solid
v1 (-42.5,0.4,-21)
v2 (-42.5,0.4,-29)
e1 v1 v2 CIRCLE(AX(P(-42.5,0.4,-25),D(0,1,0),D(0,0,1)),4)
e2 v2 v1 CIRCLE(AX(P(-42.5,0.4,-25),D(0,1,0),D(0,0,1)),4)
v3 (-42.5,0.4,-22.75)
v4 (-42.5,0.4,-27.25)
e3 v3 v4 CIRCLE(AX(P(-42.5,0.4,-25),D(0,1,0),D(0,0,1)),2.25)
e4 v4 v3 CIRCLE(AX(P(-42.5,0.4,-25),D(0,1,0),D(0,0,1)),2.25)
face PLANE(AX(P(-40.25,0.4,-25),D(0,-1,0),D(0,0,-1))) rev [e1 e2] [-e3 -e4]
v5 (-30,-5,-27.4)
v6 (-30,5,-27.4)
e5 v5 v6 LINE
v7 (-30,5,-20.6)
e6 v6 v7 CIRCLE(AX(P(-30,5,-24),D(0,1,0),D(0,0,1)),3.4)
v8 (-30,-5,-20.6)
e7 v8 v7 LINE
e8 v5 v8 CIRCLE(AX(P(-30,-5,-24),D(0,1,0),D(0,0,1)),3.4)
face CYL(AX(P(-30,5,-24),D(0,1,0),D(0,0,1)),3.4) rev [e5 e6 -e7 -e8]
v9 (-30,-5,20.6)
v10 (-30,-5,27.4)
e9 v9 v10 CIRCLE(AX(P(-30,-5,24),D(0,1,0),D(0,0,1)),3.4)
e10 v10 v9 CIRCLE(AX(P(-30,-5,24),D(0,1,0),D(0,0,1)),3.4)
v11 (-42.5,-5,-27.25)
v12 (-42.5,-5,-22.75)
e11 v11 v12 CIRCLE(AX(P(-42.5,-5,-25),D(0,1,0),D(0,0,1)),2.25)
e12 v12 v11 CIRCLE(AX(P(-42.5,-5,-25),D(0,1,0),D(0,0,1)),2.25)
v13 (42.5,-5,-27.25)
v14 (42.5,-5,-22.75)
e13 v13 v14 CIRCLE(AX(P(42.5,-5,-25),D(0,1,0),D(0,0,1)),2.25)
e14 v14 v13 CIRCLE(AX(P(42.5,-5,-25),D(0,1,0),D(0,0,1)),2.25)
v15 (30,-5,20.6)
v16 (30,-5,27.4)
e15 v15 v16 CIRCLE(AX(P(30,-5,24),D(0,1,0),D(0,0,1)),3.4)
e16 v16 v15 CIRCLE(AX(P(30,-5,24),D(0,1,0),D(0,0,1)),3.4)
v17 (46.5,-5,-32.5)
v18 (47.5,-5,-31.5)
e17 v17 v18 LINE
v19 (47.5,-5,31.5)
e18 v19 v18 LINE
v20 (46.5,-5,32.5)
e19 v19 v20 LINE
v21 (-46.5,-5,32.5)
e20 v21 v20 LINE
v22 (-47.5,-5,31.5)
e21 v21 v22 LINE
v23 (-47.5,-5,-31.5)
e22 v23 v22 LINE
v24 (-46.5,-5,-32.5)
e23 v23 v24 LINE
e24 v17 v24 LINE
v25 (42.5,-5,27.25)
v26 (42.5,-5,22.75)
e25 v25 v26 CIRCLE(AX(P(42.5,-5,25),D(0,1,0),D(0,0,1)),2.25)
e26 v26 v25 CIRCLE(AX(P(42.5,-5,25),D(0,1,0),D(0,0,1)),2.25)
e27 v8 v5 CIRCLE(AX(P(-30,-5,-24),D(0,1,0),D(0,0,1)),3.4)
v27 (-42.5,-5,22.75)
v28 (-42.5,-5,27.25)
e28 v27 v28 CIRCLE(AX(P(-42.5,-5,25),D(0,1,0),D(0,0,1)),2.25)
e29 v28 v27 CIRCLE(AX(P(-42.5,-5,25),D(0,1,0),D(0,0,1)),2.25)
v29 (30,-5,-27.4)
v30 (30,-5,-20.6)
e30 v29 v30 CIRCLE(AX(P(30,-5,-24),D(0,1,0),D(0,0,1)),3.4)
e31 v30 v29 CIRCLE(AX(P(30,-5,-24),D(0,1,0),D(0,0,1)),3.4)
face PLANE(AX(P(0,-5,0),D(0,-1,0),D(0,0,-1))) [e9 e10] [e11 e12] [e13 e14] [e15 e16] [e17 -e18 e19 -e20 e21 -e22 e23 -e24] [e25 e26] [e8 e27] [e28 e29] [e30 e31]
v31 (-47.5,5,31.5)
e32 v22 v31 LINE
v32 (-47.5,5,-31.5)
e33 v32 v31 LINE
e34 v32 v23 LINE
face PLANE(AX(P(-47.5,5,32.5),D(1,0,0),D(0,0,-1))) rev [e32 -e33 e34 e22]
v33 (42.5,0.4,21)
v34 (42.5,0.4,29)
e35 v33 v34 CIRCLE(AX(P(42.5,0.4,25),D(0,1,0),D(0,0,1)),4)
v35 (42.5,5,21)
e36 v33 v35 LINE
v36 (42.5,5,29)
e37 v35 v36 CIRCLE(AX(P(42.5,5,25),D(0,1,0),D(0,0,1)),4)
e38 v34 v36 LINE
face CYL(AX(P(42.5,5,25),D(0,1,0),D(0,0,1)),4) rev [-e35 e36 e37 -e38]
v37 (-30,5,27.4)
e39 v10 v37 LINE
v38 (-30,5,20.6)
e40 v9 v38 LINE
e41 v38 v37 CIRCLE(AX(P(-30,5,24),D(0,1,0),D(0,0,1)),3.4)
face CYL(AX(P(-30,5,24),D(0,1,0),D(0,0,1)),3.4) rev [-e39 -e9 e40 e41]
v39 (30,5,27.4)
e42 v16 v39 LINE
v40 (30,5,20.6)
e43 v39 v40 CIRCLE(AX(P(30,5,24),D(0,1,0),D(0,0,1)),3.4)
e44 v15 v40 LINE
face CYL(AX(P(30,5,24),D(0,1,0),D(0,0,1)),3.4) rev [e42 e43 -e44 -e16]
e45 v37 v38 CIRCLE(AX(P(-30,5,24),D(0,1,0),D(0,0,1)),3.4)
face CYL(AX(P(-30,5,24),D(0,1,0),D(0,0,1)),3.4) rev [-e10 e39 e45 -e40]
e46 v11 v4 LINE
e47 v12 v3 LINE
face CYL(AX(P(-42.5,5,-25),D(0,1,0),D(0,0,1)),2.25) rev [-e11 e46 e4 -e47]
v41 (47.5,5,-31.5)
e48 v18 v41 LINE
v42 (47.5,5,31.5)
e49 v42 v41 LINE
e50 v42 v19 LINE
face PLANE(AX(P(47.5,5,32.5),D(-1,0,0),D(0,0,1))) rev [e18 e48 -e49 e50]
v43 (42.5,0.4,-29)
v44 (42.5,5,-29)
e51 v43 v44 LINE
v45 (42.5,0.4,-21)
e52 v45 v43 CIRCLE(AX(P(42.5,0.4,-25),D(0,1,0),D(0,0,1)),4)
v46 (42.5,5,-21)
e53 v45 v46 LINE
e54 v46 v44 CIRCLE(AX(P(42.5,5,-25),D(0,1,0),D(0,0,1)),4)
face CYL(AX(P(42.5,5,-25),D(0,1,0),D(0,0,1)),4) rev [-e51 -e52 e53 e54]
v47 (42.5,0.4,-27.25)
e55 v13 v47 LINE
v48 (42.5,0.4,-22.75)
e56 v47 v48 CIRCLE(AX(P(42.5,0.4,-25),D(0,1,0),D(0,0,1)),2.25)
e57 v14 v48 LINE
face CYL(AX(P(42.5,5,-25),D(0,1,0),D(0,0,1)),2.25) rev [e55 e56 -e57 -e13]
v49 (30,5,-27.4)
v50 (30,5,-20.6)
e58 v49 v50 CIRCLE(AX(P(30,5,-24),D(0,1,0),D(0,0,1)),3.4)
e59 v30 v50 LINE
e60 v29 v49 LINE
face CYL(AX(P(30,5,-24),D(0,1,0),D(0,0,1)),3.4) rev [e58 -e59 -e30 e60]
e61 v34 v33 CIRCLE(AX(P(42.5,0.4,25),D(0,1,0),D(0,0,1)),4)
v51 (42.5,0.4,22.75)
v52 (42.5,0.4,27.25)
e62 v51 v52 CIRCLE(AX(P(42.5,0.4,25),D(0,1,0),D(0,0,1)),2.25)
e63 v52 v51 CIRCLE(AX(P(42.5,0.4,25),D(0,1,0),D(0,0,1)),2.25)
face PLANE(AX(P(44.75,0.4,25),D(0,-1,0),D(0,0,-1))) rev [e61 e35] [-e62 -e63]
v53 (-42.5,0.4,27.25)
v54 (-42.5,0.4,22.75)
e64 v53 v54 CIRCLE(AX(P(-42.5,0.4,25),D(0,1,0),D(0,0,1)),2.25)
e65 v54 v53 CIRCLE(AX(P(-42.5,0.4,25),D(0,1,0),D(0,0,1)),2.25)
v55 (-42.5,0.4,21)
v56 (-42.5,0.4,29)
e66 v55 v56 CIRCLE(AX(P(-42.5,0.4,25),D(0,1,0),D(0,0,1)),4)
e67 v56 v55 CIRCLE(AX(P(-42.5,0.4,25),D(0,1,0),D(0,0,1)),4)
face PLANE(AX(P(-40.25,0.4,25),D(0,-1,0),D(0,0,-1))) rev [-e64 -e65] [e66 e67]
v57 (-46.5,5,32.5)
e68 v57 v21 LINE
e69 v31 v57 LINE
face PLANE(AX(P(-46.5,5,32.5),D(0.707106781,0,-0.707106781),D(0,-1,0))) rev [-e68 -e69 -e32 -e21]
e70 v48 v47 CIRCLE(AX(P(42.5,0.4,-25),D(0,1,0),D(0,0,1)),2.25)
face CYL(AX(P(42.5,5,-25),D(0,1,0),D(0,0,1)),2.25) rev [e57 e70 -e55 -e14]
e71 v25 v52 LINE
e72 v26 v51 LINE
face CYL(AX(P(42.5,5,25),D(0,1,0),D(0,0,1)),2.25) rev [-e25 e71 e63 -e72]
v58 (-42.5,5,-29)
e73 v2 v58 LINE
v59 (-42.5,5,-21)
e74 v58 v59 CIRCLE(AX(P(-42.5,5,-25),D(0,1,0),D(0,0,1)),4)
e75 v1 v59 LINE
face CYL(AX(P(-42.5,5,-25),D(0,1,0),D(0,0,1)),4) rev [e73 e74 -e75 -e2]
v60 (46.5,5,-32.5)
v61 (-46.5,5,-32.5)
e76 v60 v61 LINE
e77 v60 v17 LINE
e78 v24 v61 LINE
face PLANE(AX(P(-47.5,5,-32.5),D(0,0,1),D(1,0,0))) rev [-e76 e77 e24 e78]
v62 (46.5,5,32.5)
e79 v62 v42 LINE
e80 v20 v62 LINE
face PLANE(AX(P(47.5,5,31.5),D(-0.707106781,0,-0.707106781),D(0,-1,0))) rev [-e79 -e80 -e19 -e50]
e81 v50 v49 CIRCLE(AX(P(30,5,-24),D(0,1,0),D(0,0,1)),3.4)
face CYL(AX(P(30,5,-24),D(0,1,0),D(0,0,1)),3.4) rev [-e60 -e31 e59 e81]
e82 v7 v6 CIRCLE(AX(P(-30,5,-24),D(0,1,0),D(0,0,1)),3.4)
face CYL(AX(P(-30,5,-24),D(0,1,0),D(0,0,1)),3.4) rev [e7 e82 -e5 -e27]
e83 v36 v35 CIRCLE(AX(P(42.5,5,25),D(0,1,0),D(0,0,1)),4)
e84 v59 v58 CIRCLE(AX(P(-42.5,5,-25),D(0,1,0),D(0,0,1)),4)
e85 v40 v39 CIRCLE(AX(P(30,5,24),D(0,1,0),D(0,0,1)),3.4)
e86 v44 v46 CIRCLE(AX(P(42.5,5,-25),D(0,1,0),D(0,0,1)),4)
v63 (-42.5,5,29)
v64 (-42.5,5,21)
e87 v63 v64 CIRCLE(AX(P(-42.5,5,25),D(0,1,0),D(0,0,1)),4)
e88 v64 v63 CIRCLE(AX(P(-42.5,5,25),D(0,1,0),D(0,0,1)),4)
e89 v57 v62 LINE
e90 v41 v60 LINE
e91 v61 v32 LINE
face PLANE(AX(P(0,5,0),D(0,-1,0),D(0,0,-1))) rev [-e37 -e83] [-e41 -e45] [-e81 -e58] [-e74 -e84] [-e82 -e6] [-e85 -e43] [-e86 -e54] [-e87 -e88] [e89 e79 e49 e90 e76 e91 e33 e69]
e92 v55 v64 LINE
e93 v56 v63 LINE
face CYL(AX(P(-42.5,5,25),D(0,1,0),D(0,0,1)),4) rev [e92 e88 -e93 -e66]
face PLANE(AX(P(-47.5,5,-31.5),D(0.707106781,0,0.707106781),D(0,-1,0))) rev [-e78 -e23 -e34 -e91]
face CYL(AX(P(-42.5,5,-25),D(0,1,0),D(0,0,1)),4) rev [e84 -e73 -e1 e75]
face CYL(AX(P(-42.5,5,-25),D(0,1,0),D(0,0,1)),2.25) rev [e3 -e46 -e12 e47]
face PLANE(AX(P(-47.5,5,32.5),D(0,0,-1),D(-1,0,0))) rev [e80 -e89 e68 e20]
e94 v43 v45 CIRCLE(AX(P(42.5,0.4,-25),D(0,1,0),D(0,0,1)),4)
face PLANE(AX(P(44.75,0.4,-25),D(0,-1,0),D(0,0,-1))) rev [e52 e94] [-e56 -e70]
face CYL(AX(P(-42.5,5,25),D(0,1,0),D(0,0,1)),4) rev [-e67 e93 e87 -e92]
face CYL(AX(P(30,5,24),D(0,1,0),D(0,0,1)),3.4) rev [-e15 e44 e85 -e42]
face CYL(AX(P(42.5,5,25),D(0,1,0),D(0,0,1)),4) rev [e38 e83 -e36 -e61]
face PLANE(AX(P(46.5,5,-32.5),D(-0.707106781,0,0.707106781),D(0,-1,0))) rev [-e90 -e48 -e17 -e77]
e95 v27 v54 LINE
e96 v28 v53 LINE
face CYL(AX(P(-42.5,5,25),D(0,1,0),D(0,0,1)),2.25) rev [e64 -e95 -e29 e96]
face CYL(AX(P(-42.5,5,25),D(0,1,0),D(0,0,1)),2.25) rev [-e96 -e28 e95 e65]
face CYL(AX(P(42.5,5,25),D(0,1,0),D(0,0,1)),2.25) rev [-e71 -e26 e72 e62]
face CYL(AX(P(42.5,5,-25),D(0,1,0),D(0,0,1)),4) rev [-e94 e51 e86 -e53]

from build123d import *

# Parameters (mm, degrees)
SKETCH_1_W                   = 95
SKETCH_1_H                   = 65
EXTRUDE_1_DEPTH              = 5
CHAMFER_1_SIZE               = 1
HOLE_WIZARD_M4_1_D           = 4.5
HOLE_WIZARD_M4_1_CBORE_D     = 8
HOLE_WIZARD_M4_1_CBORE_DEPTH = 4.6
HOLE_WIZARD_M8_1_D           = 6.8


with BuildPart() as part:
    # 草图1 → 凸台-拉伸1 (new, symmetric)
    with BuildSketch(Plane(origin=(0, 0, 0), x_dir=(1, 0, 0), z_dir=(0, 1, 0))):
        Rectangle(SKETCH_1_W, SKETCH_1_H)
    extrude(amount=EXTRUDE_1_DEPTH, both=True)

    # 倒角1
    chamfer_1_edges = [part.edges().sort_by_distance(p)[0] for p in [
        (47.5, 0, 32.5),
        (-47.5, 0, 32.5),
        (-47.5, 0, -32.5),
        (47.5, 0, -32.5),
    ]]
    chamfer(chamfer_1_edges, length=CHAMFER_1_SIZE)

    # M4 六角圆柱头螺钉的柱形沉头孔1 (through all)
    with Locations(Plane(origin=(0, 5, 0), x_dir=(1, 0, 0), z_dir=(0, 1, 0))):
        with Locations((-42.5, 25), (-42.5, -25), (42.5, -25), (42.5, 25)):
            CounterBoreHole(HOLE_WIZARD_M4_1_D / 2, HOLE_WIZARD_M4_1_CBORE_D / 2, HOLE_WIZARD_M4_1_CBORE_DEPTH)

    # M8 螺纹孔1 (through all)
    with Locations(Plane(origin=(0, 5, 0), x_dir=(1, 0, 0), z_dir=(0, 1, 0))):
        with Locations((30, 24), (30, -24), (-30, -24), (-30, 24)):
            Hole(HOLE_WIZARD_M8_1_D / 2)


solid = part.part
